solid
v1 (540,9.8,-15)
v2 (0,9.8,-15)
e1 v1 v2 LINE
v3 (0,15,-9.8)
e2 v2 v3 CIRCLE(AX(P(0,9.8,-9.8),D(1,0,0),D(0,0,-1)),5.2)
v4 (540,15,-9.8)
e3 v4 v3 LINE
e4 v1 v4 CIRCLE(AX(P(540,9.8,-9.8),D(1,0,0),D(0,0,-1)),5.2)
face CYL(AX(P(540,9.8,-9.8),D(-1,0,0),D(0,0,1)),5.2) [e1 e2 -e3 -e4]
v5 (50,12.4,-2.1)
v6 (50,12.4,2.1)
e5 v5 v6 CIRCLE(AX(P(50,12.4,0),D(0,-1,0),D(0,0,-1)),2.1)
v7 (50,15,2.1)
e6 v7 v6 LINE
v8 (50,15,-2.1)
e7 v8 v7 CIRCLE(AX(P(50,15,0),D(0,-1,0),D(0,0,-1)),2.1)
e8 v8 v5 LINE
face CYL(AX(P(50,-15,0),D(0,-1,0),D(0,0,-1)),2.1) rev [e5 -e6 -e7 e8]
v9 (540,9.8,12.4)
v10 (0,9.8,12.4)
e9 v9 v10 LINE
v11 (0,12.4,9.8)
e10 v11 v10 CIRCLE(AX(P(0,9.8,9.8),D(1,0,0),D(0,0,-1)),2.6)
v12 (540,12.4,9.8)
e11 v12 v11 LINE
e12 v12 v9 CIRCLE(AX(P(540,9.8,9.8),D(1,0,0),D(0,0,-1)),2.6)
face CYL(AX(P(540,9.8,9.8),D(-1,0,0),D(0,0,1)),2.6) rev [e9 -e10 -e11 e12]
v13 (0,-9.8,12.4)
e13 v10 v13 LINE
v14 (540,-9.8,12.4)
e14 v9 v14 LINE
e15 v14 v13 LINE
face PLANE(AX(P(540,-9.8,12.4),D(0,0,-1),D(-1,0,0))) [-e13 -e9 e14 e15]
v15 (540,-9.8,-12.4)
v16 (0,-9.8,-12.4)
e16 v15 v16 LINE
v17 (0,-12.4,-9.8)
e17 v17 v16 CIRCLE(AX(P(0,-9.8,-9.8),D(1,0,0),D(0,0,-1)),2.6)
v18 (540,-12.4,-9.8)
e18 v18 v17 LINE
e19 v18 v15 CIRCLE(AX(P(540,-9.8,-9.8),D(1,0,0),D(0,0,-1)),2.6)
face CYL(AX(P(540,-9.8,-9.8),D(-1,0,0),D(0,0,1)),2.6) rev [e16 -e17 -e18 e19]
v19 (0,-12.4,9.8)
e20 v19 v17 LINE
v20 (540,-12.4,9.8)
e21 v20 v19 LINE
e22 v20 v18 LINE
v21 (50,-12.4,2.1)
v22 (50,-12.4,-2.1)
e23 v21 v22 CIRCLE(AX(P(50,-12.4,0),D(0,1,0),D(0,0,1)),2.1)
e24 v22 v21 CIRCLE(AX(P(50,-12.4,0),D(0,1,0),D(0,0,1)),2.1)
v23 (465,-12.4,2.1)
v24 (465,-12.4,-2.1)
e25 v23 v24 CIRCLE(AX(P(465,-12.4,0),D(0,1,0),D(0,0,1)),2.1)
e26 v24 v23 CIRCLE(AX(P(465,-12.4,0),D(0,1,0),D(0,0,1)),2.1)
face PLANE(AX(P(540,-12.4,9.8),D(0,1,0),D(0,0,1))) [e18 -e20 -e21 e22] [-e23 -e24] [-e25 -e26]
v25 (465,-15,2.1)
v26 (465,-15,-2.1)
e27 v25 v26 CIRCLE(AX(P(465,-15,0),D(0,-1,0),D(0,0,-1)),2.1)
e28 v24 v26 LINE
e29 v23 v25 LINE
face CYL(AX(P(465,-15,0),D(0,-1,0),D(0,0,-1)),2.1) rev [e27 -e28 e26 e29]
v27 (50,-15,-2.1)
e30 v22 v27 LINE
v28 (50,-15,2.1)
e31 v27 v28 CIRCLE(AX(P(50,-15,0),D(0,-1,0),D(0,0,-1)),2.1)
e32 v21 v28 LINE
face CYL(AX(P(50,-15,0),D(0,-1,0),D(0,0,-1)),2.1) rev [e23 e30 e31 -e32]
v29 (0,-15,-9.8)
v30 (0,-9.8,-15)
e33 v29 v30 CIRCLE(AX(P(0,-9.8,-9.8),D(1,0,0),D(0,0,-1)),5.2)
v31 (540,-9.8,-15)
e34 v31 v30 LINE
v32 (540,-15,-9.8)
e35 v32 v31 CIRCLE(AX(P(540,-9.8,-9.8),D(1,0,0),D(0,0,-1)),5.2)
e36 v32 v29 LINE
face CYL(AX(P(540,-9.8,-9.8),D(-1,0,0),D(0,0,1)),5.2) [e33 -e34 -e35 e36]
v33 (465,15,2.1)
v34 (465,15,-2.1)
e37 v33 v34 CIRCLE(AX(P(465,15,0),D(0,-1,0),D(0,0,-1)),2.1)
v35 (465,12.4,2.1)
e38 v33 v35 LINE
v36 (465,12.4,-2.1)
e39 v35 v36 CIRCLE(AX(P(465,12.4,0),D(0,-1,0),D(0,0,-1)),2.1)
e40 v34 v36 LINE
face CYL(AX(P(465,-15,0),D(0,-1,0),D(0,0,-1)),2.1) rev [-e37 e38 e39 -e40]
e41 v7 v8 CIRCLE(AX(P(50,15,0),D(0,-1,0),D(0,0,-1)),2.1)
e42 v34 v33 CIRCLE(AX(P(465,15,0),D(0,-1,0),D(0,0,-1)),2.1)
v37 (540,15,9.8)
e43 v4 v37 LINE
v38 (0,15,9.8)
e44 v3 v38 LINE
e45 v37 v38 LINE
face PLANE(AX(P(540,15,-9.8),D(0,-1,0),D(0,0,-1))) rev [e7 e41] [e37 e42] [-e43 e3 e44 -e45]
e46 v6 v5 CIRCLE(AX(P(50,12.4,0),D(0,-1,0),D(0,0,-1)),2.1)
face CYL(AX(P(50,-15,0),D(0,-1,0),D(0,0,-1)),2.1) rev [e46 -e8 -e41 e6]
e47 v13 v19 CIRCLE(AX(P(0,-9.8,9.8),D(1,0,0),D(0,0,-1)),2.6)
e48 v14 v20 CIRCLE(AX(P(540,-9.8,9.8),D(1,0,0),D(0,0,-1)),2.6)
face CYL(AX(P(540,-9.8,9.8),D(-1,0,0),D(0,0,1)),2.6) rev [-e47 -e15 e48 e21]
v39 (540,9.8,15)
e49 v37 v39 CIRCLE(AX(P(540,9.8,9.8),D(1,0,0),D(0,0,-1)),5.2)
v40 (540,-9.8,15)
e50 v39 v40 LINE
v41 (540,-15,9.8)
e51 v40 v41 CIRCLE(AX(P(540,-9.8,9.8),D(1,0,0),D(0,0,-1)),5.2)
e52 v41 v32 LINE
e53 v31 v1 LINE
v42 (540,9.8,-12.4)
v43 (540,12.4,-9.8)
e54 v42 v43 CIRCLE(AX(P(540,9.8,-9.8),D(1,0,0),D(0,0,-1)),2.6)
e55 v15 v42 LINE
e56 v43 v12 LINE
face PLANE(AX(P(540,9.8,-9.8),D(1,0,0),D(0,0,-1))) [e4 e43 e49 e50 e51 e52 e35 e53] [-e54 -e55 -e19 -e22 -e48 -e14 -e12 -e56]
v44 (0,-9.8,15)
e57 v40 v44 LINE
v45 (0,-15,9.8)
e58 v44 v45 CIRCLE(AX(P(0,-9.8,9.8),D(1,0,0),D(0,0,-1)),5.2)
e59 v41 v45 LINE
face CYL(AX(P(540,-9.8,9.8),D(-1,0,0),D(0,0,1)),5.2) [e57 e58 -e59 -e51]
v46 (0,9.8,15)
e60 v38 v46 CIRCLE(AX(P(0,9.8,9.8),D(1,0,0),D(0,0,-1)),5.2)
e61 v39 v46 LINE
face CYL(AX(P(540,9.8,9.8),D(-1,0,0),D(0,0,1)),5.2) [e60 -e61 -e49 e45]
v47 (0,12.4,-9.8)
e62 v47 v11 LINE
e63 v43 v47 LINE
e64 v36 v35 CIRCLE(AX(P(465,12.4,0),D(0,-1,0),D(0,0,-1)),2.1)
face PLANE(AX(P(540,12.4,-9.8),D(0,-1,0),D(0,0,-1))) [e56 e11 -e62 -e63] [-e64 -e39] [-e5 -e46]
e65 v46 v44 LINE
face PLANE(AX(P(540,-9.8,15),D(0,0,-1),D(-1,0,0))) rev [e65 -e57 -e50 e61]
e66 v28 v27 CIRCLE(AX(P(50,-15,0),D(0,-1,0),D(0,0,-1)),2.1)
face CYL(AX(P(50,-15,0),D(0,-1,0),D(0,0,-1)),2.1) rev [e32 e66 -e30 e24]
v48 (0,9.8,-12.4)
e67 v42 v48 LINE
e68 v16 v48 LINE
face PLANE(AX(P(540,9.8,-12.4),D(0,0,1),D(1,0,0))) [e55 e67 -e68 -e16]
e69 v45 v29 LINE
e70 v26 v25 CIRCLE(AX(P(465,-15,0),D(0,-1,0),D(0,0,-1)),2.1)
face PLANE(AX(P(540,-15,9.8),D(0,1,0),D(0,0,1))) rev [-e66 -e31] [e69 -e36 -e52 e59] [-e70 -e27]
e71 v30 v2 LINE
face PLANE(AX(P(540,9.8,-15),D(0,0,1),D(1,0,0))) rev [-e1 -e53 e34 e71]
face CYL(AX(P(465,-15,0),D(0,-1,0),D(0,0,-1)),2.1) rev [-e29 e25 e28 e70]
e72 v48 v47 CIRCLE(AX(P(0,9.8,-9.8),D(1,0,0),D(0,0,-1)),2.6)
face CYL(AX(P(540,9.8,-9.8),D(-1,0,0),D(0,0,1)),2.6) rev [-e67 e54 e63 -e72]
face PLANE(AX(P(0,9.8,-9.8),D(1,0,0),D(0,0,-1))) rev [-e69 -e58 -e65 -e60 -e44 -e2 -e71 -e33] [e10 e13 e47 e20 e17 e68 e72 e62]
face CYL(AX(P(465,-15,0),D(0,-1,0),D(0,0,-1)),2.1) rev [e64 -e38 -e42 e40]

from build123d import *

# Parameters (mm, degrees)
MEMBER_1_DEPTH     = 540
HOLE_WIZARD_M5_1_D = 4.2
HOLE_WIZARD_2_D    = 4.2


with BuildPart() as part:
    # Sketch1 → Member 1 (new body)
    with BuildSketch(Plane(origin=(0, 0, 0), x_dir=(0, 0, -1), z_dir=(1, 0, 0))):
        with BuildLine():
            Line((-9.8, -15), (9.8, -15))
            ThreePointArc((9.8, -15), (13.476955262, -13.476955262), (15, -9.8))
            Line((15, -9.8), (15, 9.8))
            ThreePointArc((15, 9.8), (13.476955262, 13.476955262), (9.8, 15))
            Line((9.8, 15), (-9.8, 15))
            ThreePointArc((-9.8, 15), (-13.476955262, 13.476955262), (-15, 9.8))
            Line((-15, 9.8), (-15, -9.8))
            ThreePointArc((-15, -9.8), (-13.476955262, -13.476955262), (-9.8, -15))
        make_face()
        with BuildLine():
            Line((-9.8, -12.4), (9.8, -12.4))
            ThreePointArc((9.8, -12.4), (11.638477631, -11.638477631), (12.4, -9.8))
            Line((12.4, -9.8), (12.4, 9.8))
            ThreePointArc((12.4, 9.8), (11.638477631, 11.638477631), (9.8, 12.4))
            Line((9.8, 12.4), (-9.8, 12.4))
            ThreePointArc((-9.8, 12.4), (-11.638477631, 11.638477631), (-12.4, 9.8))
            Line((-12.4, 9.8), (-12.4, -9.8))
            ThreePointArc((-12.4, -9.8), (-11.638477631, -11.638477631), (-9.8, -12.4))
        make_face(mode=Mode.SUBTRACT)
    extrude(amount=MEMBER_1_DEPTH)

    # M5 螺纹孔1 (through all)
    with Locations(Plane(origin=(0, -15, 0), x_dir=(-1, 0, 0), z_dir=(0, -1, 0))):
        with Locations((-465, 0)):
            Hole(HOLE_WIZARD_M5_1_D / 2)

    # Hole Wizard 2 (through all)
    with Locations(Plane(origin=(0, -15, 0), x_dir=(-1, 0, 0), z_dir=(0, -1, 0))):
        with Locations((-50, 0)):
            Hole(HOLE_WIZARD_2_D / 2)


solid = part.part
